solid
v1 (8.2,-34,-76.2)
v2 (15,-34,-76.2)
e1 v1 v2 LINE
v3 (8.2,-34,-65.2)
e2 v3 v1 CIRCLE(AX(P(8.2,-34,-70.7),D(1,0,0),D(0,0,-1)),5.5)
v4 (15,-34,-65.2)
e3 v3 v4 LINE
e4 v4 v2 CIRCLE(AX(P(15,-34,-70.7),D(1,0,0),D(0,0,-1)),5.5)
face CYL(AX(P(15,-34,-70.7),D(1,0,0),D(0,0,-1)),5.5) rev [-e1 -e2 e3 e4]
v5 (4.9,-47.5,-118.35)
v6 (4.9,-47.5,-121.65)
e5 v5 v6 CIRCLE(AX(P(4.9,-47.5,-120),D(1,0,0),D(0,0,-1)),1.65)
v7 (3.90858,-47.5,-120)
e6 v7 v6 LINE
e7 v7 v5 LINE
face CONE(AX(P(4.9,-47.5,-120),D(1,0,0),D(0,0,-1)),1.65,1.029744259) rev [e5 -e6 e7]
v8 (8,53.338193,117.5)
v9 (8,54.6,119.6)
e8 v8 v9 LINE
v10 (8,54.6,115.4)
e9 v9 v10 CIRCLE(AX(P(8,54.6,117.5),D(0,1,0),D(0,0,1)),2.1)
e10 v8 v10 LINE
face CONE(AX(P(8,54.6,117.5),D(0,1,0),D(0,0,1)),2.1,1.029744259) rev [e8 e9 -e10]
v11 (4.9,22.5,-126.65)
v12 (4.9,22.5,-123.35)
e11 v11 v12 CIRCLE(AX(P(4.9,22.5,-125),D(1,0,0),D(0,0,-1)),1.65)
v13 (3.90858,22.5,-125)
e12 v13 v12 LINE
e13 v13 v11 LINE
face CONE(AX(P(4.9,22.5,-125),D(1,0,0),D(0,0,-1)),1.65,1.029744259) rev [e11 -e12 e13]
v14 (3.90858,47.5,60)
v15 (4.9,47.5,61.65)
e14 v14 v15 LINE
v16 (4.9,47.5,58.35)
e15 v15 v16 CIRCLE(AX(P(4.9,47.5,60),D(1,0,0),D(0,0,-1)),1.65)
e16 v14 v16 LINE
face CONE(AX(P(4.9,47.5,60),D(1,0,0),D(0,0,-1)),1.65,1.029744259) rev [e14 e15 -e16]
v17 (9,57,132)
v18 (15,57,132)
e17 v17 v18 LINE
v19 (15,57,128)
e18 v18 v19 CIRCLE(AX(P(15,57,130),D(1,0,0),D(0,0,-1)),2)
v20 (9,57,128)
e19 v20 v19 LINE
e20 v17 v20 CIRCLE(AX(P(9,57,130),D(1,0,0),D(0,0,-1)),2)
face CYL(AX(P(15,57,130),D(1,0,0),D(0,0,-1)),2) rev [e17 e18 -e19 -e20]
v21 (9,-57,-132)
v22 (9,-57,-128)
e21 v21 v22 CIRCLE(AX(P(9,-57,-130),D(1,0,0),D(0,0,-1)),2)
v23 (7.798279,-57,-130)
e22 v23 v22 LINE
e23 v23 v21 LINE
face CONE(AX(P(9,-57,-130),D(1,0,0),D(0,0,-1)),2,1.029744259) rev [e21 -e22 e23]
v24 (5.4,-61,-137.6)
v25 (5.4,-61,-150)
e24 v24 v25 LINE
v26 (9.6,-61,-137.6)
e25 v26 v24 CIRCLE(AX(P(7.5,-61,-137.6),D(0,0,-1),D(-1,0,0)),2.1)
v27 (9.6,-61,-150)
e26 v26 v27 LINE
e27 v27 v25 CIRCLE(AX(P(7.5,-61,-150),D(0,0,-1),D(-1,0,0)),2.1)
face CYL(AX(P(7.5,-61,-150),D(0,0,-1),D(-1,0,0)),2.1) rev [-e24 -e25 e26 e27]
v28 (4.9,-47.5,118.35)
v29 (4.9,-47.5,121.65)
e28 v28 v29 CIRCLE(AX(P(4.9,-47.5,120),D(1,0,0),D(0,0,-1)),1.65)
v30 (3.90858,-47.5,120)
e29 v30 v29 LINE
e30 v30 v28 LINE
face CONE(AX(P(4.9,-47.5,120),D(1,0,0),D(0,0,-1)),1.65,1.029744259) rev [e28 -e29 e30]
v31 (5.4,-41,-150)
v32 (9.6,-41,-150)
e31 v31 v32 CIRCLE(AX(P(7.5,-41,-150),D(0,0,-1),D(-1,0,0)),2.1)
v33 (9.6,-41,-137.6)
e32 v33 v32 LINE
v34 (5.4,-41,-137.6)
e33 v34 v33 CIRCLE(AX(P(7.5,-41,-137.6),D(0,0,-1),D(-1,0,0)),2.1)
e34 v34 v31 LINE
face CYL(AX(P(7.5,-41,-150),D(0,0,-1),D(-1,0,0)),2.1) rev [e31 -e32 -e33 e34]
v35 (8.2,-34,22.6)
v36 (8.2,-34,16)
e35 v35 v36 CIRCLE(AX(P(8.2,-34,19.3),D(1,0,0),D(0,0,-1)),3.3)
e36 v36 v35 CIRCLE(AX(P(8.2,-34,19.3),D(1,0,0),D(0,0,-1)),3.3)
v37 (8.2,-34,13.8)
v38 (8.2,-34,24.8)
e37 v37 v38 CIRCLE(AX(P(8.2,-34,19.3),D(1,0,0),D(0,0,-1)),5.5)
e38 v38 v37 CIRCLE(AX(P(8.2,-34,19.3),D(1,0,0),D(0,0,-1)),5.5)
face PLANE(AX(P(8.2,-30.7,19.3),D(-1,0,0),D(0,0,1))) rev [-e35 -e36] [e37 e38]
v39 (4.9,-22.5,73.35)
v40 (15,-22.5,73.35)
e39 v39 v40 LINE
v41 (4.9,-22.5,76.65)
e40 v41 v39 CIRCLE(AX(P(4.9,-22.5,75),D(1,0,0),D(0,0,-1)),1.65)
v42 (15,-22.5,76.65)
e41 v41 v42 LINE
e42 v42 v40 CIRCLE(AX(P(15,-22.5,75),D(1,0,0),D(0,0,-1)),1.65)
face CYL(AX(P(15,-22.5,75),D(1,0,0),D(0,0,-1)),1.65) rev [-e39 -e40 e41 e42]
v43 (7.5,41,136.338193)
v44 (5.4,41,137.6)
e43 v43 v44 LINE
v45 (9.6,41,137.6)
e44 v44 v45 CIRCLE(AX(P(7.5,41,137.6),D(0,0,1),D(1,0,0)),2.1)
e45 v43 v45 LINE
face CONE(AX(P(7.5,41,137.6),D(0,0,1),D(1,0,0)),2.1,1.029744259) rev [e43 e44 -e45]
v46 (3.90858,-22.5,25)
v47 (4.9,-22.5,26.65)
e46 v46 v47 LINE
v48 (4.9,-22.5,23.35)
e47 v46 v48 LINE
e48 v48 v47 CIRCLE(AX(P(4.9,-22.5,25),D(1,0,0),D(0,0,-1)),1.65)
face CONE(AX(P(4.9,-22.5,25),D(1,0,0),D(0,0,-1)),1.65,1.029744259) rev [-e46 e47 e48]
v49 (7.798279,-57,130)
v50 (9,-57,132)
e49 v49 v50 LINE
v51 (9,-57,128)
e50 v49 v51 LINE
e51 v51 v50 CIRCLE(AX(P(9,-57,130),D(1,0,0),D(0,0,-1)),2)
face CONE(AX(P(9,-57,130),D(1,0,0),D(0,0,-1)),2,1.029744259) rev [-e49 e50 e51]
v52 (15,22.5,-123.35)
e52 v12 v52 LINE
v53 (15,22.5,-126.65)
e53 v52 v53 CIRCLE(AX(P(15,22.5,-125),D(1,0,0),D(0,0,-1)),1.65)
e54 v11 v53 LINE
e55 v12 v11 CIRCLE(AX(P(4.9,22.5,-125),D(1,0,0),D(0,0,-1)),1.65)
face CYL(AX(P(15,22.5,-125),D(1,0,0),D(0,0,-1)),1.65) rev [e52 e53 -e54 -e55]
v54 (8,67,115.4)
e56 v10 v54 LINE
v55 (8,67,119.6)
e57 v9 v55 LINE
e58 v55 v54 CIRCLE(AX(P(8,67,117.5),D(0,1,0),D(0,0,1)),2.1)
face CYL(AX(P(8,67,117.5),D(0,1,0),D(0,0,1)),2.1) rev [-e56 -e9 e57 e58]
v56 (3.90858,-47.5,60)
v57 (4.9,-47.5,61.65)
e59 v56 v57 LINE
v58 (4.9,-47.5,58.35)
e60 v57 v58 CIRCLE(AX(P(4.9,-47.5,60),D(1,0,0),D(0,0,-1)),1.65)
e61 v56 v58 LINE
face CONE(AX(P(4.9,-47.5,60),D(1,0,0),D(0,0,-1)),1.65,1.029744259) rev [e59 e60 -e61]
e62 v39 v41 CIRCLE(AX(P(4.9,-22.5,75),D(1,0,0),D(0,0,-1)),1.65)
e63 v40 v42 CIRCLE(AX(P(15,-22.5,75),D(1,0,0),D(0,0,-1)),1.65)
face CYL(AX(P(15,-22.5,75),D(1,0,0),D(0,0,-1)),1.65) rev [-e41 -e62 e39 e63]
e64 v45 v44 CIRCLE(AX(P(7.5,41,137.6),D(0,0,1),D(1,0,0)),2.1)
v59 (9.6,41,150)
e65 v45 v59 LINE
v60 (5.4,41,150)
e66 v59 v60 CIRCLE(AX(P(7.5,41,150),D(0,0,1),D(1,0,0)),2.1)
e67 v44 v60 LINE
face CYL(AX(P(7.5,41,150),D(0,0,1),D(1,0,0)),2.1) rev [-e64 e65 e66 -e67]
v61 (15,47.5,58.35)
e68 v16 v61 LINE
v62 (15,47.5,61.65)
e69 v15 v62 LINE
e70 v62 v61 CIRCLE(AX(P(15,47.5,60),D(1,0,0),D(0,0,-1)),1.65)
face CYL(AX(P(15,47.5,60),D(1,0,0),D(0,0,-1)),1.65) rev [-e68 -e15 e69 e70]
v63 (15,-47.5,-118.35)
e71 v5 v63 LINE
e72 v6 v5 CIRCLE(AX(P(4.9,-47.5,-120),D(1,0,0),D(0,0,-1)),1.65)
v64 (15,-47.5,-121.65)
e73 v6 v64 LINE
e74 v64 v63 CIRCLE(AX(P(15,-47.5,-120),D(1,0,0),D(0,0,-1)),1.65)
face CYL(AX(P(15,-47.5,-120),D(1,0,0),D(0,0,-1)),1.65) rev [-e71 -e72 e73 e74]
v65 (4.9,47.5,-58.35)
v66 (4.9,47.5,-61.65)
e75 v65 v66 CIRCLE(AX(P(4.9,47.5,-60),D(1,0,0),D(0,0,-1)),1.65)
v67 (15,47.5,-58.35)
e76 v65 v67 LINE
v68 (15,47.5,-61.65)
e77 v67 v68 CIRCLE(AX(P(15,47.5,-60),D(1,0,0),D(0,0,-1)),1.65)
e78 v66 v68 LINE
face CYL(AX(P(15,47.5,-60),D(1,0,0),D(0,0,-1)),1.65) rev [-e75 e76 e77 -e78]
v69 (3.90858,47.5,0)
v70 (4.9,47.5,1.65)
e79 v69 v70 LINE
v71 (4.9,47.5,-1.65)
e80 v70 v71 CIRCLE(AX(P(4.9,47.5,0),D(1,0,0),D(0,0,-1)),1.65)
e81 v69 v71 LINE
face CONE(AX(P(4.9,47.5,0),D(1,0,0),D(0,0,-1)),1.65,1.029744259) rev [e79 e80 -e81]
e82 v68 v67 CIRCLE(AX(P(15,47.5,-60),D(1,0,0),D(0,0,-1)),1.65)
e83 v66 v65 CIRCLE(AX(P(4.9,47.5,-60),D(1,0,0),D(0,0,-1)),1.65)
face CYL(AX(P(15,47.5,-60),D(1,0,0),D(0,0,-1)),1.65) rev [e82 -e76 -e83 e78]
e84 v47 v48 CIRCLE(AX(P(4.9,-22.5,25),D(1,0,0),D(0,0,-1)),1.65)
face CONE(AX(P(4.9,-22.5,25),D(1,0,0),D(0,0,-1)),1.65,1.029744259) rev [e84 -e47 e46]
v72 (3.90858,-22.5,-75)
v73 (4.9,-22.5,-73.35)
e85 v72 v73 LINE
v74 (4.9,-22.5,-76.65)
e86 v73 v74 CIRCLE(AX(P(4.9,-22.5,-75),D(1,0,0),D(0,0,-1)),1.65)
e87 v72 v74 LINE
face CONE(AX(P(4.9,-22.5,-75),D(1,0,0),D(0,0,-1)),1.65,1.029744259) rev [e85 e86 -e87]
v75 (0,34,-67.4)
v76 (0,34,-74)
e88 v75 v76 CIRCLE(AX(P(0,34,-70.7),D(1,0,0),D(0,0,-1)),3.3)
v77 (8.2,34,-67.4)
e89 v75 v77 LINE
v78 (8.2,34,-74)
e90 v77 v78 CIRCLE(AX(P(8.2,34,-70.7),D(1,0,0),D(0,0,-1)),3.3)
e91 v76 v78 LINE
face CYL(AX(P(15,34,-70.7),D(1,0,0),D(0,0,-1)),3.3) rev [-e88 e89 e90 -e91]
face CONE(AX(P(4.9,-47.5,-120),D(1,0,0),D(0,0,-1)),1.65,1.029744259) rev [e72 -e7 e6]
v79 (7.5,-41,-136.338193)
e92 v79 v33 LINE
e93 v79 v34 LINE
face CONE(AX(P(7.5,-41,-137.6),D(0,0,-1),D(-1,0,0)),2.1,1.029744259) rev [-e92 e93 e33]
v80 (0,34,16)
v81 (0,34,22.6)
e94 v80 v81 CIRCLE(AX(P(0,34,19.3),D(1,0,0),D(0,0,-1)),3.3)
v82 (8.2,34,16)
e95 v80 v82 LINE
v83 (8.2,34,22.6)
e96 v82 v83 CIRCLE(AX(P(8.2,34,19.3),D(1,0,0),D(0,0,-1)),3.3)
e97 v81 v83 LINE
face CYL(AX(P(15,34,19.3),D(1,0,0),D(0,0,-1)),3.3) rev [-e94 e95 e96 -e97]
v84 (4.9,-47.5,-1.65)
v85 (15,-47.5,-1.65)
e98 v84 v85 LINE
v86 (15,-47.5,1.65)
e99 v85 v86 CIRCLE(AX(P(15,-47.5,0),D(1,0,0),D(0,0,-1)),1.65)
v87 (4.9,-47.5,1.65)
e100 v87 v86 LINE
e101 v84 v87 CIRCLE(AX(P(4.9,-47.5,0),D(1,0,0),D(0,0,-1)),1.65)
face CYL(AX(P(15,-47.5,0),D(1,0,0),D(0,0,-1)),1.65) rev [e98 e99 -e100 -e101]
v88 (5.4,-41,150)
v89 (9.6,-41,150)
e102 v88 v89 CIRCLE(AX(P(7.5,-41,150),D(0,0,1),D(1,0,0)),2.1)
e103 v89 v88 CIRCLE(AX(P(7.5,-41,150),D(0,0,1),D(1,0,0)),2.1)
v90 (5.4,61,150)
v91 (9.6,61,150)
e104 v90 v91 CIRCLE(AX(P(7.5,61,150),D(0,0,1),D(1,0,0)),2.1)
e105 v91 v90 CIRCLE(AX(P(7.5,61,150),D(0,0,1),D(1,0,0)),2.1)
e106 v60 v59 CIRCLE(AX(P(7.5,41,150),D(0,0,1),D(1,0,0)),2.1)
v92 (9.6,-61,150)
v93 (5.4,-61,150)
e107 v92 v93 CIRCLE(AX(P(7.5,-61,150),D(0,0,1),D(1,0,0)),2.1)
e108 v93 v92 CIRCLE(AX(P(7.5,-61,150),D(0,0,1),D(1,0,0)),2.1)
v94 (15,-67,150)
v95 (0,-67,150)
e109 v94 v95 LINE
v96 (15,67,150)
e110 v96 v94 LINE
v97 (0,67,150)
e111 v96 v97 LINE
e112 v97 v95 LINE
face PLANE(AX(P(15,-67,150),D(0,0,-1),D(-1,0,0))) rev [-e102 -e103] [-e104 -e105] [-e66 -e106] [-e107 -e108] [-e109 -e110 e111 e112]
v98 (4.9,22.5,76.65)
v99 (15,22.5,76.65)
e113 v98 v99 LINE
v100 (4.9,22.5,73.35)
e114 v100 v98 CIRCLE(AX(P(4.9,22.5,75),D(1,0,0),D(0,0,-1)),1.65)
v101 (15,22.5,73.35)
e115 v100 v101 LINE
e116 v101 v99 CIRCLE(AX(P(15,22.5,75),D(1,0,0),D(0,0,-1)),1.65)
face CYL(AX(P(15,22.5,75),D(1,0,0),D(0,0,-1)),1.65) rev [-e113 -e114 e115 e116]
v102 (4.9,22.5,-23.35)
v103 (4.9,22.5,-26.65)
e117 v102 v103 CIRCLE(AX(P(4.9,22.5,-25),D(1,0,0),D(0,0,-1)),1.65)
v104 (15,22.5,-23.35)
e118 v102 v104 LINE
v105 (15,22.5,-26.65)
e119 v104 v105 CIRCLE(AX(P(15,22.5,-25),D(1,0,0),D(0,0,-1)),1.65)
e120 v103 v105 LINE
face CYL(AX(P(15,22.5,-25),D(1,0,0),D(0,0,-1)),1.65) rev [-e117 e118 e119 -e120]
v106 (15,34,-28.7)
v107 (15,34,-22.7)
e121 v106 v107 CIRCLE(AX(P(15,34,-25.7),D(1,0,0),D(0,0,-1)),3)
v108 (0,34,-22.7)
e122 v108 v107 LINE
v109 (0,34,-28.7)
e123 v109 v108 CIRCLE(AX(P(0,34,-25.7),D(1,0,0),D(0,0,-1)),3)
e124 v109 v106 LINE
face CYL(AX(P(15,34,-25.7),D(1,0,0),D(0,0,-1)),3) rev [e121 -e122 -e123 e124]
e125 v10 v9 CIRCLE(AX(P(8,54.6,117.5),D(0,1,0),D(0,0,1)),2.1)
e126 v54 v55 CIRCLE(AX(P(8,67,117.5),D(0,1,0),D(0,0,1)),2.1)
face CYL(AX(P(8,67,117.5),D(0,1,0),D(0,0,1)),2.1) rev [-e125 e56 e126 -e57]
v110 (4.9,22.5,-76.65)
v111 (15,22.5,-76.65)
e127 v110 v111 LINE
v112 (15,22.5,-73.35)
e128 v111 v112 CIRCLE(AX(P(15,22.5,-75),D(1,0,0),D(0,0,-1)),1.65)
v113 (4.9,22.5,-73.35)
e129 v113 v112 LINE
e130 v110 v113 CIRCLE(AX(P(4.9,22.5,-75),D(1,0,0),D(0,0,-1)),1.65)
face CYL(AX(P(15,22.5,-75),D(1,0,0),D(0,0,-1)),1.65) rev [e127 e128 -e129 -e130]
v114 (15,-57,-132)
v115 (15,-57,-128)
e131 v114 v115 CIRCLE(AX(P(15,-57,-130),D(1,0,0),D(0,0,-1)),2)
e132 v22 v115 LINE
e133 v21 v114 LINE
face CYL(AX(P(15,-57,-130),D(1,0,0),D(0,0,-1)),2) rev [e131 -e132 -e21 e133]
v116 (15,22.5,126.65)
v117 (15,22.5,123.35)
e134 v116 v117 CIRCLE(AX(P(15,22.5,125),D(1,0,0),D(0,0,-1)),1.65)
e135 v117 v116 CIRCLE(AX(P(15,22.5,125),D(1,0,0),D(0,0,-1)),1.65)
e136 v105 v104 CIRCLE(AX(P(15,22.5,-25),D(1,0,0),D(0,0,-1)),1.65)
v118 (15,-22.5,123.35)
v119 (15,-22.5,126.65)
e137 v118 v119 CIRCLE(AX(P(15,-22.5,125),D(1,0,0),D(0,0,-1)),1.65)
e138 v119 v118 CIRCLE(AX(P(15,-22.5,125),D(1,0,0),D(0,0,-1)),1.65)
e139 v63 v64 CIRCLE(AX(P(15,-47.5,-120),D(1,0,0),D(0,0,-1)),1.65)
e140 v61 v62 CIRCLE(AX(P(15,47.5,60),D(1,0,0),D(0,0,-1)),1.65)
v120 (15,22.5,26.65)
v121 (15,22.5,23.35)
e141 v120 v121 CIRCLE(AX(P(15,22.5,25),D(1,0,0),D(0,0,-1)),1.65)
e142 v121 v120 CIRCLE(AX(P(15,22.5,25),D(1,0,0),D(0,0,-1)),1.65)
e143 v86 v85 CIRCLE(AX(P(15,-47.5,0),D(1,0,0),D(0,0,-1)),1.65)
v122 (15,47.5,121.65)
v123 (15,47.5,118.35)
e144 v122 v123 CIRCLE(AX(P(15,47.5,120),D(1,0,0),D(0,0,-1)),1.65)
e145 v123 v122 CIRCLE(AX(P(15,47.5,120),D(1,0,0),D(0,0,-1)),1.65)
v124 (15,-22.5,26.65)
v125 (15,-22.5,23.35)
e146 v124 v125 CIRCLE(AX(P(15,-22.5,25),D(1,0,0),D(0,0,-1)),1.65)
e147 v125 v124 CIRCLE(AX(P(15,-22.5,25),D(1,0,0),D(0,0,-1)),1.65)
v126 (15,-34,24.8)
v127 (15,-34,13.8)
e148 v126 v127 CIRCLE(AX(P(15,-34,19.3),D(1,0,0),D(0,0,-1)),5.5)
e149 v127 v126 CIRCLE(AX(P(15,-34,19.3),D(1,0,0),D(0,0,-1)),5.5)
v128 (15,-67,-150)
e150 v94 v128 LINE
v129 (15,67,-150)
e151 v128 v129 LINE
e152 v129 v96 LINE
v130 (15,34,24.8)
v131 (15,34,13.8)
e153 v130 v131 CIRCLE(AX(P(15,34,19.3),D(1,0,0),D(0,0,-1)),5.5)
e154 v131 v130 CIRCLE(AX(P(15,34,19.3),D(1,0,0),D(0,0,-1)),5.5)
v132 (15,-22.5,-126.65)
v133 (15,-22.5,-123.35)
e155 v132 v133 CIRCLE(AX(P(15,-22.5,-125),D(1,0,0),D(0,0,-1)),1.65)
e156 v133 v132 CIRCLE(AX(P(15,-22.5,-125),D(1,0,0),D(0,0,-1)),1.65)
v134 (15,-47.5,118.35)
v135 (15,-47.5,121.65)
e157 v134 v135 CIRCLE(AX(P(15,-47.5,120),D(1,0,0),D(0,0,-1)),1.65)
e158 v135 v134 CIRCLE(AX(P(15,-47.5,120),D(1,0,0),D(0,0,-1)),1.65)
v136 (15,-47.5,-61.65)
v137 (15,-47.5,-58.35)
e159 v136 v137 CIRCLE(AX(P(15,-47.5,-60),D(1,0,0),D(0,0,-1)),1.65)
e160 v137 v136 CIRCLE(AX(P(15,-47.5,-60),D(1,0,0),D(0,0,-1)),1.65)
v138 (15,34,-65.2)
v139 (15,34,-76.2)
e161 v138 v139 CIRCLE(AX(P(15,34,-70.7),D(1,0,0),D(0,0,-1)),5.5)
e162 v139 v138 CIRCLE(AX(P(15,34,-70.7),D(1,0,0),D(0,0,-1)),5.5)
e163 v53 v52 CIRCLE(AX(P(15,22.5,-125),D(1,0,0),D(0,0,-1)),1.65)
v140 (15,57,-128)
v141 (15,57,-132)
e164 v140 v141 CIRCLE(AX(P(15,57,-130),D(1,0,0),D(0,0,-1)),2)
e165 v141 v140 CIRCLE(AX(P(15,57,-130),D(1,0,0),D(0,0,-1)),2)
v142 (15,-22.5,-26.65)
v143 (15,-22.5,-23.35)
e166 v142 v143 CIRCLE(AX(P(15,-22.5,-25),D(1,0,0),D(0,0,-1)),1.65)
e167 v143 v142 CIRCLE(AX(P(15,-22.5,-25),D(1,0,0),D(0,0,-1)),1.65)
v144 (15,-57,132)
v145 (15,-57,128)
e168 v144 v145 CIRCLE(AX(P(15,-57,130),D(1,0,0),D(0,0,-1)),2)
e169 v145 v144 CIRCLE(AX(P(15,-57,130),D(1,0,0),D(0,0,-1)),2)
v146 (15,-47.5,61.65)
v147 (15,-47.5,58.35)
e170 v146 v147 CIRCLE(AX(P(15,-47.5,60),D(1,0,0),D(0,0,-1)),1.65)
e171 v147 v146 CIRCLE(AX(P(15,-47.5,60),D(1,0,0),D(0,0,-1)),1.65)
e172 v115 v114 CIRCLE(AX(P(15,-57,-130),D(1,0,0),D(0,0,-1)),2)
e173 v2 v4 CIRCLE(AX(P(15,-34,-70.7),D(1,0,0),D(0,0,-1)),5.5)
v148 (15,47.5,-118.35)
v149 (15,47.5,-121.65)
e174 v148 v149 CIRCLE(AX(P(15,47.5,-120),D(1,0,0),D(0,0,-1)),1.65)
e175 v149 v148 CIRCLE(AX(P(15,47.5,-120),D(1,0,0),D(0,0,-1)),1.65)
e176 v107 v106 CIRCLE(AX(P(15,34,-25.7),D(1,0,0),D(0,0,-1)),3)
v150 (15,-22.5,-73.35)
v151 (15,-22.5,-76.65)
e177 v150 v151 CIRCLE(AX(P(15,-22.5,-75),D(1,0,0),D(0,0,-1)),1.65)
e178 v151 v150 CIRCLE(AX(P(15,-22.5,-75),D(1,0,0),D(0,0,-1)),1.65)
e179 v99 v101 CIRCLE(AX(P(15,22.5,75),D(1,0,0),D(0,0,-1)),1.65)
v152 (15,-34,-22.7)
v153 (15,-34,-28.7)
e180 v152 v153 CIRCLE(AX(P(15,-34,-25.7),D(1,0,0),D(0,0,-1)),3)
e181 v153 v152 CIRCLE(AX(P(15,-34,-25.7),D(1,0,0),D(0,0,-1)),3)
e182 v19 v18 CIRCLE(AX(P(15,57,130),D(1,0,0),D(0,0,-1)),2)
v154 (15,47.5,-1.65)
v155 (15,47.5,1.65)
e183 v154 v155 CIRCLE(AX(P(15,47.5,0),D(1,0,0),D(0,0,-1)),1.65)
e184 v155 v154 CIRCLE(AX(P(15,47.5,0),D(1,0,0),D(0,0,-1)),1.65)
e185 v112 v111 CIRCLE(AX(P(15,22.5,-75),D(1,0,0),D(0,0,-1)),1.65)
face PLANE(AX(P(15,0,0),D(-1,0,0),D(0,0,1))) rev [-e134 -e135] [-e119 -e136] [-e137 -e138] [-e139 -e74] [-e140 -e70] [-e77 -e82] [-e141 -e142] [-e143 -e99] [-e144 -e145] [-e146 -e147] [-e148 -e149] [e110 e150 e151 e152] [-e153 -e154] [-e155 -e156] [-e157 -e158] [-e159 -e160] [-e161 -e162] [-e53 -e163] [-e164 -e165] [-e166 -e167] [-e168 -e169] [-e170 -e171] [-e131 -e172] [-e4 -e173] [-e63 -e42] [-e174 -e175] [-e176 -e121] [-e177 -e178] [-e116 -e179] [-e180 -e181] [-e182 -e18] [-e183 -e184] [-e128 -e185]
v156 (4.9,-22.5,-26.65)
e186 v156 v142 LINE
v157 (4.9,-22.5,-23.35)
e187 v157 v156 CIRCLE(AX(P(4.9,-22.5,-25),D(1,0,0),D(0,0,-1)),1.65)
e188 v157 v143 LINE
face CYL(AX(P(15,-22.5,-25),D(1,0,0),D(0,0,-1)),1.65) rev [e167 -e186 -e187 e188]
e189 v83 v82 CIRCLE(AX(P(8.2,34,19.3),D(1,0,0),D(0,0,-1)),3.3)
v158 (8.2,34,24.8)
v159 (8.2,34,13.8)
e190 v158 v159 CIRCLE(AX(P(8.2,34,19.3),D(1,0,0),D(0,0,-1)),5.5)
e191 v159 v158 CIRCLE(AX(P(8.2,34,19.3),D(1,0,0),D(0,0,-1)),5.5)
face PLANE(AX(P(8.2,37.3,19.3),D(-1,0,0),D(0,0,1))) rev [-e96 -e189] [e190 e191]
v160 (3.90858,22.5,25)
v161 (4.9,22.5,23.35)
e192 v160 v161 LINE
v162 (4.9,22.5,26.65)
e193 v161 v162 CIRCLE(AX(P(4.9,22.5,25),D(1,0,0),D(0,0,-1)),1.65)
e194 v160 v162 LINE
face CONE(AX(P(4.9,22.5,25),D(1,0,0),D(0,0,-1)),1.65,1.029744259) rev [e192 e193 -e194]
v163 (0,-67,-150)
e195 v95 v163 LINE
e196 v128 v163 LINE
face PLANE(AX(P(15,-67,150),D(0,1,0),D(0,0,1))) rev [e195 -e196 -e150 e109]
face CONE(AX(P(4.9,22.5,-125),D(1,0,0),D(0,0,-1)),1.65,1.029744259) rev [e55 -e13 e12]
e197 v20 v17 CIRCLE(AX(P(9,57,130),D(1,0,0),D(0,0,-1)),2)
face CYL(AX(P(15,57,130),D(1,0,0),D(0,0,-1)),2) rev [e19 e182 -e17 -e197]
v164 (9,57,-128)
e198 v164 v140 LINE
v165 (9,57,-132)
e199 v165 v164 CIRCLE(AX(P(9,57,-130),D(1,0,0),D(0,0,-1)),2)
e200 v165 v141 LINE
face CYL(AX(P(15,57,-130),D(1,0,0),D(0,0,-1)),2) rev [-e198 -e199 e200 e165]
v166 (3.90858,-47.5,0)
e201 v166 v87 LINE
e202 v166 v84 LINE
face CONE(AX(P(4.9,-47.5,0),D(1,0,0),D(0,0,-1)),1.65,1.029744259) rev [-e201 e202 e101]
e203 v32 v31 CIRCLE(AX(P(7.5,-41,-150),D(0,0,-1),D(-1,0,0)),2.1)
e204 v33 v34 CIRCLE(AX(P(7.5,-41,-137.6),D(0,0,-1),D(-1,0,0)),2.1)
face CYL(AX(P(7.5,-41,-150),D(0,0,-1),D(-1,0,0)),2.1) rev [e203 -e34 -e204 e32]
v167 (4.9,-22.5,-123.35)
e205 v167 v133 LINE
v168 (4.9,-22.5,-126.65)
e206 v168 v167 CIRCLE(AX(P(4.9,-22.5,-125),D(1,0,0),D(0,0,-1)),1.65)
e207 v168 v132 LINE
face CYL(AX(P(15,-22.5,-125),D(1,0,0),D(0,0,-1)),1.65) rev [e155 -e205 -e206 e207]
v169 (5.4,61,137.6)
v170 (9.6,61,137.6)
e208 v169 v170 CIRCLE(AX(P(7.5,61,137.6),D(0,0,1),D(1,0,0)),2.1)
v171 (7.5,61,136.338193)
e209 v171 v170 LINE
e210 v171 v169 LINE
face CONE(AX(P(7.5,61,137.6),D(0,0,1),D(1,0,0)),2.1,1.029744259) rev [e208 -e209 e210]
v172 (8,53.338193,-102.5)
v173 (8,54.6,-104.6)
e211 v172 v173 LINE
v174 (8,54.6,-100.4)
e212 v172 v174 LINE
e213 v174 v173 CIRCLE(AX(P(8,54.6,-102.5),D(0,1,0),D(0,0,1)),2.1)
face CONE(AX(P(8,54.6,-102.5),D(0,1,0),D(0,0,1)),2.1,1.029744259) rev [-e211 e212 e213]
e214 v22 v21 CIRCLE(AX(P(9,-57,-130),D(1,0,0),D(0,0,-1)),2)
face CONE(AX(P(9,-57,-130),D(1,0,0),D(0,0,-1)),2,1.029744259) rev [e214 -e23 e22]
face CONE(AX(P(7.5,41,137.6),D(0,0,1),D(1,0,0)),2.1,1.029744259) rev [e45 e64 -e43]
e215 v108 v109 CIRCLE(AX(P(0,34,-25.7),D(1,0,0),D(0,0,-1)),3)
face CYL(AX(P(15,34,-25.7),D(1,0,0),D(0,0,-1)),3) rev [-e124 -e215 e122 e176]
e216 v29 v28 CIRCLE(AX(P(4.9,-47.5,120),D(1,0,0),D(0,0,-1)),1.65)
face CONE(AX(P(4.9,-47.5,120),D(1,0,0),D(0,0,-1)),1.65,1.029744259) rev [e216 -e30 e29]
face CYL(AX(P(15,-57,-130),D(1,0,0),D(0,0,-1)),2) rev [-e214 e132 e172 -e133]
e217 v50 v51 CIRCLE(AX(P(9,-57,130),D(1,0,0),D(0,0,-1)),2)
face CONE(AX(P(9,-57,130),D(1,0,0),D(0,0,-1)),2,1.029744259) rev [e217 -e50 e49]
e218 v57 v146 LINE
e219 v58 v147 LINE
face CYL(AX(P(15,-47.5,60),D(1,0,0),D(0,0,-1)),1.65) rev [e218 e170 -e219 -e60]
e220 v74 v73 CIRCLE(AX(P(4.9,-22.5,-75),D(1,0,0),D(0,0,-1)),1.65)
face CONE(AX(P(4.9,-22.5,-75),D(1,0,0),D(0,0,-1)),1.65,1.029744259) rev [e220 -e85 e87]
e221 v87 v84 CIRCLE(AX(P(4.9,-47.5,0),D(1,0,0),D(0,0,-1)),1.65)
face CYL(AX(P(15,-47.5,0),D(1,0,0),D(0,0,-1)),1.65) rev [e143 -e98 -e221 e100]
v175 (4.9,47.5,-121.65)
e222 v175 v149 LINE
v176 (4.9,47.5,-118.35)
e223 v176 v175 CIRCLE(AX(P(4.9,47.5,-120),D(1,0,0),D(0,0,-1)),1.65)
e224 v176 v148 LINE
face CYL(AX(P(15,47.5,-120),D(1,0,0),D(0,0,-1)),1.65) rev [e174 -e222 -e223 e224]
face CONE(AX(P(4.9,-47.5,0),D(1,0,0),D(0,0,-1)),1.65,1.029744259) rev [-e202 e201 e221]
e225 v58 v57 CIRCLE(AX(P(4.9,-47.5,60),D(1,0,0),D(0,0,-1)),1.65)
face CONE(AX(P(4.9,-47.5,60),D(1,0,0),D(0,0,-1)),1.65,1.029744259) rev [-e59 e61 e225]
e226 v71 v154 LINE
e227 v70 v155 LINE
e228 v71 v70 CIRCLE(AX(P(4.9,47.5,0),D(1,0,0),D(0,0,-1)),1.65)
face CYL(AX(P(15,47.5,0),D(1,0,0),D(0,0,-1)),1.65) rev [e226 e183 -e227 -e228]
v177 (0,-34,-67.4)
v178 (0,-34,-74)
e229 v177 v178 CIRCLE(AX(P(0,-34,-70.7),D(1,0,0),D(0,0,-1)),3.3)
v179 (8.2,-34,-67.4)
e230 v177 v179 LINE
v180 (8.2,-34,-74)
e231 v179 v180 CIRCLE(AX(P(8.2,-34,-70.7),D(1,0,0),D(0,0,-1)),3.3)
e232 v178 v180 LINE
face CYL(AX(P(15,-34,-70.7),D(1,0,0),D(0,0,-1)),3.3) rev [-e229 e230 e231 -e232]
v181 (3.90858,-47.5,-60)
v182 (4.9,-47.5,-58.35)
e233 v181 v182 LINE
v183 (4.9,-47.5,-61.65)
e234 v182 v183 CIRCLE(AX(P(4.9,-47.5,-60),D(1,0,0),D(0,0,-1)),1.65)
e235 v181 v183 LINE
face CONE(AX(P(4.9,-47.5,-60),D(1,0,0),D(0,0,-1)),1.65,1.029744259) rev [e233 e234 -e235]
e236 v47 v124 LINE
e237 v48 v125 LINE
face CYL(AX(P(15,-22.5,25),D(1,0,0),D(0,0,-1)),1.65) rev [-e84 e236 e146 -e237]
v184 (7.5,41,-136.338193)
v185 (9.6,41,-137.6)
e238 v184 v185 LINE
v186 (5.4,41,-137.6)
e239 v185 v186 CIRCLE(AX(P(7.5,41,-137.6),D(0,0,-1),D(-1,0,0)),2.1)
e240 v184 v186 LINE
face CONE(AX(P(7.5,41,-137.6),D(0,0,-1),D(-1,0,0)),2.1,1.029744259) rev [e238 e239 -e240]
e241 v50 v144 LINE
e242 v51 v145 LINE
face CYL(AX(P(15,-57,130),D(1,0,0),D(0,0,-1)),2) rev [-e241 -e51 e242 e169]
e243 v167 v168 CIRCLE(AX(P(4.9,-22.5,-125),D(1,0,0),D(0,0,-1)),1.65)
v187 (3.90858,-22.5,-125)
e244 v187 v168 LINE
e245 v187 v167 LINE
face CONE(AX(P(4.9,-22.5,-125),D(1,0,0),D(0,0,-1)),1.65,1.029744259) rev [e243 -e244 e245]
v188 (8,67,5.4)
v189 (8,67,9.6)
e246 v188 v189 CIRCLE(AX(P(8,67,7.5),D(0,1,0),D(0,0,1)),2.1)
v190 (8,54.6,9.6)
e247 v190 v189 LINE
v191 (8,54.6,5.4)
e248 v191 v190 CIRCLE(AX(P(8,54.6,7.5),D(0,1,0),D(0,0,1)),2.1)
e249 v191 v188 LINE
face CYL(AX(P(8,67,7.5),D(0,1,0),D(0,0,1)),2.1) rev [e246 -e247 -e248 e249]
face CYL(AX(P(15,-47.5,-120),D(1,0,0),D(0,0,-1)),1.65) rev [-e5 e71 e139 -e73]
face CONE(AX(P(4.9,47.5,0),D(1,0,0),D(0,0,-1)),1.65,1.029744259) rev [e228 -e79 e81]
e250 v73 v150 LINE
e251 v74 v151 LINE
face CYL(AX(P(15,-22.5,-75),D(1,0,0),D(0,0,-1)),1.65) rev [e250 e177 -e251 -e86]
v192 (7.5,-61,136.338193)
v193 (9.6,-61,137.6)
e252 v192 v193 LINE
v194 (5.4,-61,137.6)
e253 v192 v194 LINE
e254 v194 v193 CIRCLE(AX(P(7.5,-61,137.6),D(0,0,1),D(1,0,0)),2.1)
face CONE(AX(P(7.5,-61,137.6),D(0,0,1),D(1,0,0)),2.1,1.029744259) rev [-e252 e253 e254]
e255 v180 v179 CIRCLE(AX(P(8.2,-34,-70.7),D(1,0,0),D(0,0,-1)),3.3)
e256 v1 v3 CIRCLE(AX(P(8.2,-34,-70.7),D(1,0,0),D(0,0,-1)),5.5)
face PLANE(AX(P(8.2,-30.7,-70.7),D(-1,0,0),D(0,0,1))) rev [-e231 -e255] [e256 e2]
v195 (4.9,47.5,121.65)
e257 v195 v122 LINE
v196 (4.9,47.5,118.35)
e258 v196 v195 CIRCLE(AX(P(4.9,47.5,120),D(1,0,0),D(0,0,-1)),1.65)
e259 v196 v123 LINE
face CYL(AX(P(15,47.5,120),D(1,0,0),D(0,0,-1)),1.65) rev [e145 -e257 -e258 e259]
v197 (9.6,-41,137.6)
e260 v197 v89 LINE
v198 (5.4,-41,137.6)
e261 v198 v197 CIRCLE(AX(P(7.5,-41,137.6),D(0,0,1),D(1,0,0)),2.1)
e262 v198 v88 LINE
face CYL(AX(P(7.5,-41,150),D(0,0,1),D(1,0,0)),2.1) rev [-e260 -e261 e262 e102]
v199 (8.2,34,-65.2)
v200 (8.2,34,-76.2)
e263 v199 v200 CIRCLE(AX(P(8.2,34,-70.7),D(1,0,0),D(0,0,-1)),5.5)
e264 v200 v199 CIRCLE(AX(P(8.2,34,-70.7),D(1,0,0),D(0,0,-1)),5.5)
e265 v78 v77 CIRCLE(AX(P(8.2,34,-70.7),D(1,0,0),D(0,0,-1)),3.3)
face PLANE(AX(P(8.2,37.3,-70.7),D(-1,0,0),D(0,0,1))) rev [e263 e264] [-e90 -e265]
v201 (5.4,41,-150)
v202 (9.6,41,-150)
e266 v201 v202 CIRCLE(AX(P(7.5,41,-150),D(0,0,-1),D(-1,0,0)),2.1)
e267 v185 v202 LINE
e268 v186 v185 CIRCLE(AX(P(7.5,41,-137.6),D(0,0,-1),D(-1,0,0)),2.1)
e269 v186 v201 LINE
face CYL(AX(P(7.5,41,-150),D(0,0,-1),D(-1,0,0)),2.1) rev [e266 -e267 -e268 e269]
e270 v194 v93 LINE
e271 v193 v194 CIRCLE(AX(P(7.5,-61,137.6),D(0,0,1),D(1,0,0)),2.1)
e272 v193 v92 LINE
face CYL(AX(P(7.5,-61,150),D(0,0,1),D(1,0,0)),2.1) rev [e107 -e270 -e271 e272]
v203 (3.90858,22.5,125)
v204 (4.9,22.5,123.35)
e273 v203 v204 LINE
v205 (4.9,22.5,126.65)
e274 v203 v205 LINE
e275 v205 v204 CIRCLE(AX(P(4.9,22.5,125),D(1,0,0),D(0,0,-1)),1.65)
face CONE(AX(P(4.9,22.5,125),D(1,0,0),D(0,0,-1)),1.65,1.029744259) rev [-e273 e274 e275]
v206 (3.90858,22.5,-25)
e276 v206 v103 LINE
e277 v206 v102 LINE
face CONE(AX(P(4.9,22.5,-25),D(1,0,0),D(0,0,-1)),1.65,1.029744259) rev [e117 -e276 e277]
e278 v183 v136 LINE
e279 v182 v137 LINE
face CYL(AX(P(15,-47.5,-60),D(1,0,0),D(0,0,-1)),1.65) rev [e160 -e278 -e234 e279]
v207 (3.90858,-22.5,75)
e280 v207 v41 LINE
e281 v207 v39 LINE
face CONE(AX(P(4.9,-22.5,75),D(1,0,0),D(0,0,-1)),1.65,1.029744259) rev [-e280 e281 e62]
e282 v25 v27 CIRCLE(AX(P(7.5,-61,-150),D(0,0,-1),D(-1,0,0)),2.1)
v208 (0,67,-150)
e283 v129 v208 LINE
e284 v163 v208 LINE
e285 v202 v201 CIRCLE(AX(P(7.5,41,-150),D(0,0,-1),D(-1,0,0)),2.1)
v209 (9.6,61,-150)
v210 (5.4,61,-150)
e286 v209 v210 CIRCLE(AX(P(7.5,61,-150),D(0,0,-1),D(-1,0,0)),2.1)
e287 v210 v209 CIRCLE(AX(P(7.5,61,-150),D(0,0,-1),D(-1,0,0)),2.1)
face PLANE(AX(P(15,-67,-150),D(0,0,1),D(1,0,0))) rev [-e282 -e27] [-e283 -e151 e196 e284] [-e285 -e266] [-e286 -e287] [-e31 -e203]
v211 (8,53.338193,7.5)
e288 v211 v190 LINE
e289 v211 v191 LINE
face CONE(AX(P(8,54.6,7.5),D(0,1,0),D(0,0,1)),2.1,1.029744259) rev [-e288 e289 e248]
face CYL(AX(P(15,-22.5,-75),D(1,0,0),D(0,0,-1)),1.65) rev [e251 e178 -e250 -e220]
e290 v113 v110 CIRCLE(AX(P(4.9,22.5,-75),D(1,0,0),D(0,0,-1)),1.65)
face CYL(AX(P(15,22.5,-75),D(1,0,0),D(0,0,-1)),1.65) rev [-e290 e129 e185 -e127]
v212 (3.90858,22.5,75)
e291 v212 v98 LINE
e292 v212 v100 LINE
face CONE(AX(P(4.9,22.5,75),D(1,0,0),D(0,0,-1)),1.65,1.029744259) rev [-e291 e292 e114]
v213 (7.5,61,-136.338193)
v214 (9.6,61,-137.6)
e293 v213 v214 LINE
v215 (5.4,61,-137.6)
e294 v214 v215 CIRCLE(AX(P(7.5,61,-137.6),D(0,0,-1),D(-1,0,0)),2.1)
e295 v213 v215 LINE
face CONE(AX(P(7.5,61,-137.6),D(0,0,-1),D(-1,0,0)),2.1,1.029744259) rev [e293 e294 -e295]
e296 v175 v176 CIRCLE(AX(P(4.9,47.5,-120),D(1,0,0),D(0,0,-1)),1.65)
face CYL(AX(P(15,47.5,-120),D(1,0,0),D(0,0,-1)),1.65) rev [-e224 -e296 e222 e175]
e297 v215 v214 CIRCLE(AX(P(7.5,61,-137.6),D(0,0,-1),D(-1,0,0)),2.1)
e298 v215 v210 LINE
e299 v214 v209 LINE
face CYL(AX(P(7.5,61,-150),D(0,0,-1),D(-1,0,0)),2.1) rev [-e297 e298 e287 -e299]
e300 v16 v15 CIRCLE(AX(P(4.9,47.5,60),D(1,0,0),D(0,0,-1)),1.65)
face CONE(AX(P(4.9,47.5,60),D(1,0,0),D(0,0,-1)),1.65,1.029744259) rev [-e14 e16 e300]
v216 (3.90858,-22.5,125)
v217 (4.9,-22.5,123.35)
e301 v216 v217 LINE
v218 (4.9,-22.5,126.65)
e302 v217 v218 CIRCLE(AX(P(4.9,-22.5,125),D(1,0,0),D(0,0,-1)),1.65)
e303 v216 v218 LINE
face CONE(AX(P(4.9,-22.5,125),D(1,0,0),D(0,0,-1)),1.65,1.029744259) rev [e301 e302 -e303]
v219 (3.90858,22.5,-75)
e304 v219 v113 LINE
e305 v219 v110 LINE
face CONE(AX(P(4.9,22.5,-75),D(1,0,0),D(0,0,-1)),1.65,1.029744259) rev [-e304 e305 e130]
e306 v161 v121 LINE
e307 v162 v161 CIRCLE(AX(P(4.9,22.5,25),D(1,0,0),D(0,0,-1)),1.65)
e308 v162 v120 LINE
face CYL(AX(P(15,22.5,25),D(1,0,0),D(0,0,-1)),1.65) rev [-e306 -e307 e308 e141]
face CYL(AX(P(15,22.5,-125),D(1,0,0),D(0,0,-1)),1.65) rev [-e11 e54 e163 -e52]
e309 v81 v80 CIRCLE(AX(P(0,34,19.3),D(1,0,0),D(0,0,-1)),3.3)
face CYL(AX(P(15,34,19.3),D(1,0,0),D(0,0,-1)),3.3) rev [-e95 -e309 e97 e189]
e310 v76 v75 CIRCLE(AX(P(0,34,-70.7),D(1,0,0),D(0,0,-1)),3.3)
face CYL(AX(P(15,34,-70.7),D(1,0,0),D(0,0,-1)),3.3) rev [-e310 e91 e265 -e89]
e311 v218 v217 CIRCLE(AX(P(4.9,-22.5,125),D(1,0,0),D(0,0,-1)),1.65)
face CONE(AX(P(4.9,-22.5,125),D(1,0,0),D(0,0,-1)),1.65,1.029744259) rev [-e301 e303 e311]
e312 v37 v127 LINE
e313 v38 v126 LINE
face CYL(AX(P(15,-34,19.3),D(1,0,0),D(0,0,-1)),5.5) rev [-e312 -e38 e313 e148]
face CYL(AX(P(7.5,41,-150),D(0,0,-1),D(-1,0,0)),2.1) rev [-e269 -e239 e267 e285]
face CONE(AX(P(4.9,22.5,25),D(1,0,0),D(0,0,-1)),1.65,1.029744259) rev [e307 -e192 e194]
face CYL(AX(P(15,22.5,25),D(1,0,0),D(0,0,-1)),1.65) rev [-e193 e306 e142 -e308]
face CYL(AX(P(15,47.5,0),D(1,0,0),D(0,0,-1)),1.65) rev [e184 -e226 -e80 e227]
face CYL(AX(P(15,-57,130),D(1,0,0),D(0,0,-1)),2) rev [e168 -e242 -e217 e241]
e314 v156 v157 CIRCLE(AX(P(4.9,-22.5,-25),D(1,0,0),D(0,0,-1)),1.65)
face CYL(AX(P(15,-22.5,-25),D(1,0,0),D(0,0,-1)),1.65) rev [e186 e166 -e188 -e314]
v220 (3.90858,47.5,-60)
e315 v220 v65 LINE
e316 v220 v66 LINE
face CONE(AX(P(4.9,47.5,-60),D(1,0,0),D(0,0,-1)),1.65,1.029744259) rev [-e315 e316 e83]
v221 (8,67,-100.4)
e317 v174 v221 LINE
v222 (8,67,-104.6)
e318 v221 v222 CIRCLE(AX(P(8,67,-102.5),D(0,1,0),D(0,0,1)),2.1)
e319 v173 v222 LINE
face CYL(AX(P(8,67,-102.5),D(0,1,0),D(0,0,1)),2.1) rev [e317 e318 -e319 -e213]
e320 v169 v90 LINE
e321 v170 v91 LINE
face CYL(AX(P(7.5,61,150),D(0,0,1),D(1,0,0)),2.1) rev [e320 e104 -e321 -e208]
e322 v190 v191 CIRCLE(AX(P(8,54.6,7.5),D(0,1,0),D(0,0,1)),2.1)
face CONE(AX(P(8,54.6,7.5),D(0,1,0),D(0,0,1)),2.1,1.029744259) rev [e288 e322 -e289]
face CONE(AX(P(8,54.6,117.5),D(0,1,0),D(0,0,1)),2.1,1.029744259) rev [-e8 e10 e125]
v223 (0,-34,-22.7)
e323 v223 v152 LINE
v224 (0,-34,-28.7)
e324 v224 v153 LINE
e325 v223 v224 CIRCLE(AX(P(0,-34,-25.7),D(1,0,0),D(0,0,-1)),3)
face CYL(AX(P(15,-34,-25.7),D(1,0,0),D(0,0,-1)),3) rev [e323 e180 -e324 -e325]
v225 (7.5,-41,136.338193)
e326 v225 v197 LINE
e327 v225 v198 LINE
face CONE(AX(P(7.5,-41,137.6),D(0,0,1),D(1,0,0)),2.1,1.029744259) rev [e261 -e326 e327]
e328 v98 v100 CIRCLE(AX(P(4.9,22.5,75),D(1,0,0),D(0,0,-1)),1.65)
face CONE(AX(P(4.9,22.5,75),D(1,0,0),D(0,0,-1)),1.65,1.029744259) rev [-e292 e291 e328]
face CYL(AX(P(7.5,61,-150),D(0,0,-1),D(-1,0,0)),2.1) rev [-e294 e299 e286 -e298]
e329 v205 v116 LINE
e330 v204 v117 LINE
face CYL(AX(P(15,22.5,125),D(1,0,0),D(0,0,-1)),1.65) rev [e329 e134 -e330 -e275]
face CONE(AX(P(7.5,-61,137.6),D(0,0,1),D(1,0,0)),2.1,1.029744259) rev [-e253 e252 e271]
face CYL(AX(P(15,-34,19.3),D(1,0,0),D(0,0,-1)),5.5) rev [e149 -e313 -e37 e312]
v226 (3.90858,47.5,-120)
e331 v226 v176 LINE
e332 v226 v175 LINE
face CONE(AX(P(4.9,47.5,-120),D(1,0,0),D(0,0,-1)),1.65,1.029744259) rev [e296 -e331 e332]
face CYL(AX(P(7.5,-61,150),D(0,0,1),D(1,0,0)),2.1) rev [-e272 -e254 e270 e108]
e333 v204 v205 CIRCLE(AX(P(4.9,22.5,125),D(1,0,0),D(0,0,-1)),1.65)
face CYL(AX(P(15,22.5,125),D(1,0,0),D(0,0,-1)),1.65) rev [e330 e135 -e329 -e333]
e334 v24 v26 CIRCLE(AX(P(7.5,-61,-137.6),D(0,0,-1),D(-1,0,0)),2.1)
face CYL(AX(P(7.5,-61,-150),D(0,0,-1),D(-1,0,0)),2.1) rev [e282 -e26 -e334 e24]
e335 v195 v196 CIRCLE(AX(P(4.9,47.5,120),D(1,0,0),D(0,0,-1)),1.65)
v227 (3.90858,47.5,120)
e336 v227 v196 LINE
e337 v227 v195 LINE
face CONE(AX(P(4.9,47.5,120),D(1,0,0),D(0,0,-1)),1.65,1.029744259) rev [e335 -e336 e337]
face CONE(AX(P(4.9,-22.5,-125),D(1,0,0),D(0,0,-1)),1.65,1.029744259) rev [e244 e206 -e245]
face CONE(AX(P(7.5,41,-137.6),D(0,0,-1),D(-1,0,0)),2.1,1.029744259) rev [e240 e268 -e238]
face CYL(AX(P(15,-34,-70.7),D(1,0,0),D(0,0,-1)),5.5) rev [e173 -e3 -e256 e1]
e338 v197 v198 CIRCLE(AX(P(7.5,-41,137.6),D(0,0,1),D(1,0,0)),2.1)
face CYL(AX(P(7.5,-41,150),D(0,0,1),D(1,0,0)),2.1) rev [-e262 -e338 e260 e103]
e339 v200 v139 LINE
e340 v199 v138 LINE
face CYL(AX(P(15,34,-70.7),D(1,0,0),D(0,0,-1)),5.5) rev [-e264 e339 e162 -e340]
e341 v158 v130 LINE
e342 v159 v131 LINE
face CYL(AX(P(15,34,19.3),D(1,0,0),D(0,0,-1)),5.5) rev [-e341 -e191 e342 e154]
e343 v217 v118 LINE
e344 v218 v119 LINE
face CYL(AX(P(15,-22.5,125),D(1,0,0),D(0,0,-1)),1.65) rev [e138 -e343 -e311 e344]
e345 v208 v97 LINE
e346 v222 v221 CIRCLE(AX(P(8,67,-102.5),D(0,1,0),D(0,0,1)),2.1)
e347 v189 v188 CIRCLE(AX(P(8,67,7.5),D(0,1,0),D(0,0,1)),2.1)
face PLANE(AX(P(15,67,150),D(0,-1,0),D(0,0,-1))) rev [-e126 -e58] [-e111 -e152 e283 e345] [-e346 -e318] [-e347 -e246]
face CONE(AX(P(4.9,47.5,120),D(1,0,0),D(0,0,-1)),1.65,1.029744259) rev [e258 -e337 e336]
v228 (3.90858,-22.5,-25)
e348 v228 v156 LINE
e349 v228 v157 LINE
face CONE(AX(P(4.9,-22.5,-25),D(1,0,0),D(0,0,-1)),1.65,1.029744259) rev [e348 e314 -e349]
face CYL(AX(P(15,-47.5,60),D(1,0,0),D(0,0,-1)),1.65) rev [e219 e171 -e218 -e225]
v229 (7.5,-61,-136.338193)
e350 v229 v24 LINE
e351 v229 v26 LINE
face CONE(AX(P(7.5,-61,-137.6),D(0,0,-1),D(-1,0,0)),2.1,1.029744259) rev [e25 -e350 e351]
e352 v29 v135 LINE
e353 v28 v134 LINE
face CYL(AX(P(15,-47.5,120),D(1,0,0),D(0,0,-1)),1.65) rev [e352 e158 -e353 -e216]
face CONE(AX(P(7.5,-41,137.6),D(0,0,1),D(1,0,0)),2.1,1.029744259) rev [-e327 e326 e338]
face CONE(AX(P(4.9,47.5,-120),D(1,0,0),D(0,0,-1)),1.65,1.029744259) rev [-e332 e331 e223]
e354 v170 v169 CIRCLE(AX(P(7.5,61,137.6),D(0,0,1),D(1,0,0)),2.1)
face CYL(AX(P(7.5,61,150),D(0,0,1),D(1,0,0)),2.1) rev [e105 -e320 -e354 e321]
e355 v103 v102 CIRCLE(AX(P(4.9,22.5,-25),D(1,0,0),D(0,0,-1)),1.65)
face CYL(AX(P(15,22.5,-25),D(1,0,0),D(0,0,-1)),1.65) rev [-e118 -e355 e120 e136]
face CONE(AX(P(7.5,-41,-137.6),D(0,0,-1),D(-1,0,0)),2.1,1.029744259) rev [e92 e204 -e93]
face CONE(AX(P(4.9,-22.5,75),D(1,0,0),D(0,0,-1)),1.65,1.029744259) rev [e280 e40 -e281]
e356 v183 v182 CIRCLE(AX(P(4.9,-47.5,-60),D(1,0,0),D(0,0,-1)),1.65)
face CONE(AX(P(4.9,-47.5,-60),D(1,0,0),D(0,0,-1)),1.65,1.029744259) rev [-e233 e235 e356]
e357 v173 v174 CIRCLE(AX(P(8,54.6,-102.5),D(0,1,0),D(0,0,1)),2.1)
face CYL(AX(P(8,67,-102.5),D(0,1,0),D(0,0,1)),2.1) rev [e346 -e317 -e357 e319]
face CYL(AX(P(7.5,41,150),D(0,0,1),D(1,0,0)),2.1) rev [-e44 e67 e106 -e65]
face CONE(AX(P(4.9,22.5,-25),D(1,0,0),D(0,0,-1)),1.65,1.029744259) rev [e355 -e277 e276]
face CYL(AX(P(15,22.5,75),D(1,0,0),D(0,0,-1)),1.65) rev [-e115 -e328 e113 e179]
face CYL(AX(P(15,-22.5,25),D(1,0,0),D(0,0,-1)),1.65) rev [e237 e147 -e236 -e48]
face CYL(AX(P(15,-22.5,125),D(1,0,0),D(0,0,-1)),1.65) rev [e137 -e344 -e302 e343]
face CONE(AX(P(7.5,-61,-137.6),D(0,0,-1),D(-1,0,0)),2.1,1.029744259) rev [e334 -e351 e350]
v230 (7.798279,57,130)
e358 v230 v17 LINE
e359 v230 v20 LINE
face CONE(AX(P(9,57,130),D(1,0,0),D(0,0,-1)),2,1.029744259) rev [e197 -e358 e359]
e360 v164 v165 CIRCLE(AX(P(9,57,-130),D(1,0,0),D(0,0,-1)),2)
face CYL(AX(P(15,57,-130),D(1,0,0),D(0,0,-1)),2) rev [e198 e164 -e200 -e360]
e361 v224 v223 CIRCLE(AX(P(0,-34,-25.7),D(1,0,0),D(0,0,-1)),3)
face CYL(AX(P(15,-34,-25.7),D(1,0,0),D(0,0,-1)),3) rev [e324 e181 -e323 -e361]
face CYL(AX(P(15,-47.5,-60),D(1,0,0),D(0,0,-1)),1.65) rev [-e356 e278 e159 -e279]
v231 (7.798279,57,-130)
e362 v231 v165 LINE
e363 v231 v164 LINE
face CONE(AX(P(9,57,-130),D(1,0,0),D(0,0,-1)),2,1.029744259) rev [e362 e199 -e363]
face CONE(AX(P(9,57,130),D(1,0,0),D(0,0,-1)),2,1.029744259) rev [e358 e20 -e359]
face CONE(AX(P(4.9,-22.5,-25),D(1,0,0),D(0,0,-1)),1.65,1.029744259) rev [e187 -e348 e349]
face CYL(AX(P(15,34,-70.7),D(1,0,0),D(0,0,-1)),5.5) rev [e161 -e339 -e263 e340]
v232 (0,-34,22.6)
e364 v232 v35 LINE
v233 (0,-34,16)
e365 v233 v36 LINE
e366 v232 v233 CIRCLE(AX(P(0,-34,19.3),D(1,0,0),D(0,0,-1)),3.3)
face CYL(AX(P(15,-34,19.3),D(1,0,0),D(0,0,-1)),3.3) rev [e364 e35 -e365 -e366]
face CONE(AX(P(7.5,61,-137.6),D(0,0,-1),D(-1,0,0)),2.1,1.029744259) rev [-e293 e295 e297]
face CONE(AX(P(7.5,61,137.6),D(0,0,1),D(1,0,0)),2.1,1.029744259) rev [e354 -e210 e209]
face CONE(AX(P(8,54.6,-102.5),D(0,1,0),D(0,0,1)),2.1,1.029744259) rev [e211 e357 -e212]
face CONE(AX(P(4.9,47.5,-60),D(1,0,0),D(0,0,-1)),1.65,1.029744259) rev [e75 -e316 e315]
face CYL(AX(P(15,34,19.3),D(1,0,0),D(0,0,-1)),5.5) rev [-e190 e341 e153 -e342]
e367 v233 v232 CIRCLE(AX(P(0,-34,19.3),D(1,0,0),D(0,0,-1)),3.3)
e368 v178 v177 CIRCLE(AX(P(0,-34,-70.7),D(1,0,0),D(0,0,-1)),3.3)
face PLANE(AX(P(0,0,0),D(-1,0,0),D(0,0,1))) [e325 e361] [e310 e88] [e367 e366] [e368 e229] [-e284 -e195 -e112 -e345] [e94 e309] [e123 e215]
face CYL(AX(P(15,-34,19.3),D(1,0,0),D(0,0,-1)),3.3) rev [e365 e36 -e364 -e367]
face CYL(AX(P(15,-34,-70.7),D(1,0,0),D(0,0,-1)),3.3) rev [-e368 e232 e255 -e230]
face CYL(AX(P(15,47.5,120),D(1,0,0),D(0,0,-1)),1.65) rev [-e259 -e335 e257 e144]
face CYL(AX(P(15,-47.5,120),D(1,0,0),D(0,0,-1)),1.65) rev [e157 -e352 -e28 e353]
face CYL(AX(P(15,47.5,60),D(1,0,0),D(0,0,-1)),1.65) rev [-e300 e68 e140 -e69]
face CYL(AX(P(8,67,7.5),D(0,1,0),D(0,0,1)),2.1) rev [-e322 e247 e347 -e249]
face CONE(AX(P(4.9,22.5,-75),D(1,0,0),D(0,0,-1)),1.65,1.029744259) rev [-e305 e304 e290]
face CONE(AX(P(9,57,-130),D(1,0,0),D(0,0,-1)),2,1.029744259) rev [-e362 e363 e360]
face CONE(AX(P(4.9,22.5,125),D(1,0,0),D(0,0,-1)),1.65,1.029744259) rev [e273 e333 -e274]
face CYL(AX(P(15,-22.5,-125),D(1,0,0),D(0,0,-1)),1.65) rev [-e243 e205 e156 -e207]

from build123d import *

# Parameters (mm, degrees)
SKETCH1_W                                            = 300
SKETCH1_H                                            = 134
BOSS_EXTRUDE1_DEPTH                                  = 15
M4_TAPPED_HOLE1_D                                    = 3.3
M4_TAPPED_HOLE1_DEPTH                                = 10.1
M4_TAPPED_HOLE1_TIP                                  = 0.991420021
M4_TAPPED_HOLE2_D                                    = 3.3
M4_TAPPED_HOLE2_DEPTH                                = 10.1
M4_TAPPED_HOLE2_TIP                                  = 0.991420021
M5_TAPPED_HOLE1_AT_2_COUNT                           = 2
M5_TAPPED_HOLE1_AT_2_PITCH                           = 20
M5_TAPPED_HOLE1_AT_3_COUNT                           = 2
M5_TAPPED_HOLE1_AT_3_PITCH                           = 102
M5_TAPPED_HOLE1_AT_4_COUNT                           = 2
M5_TAPPED_HOLE1_AT_4_PITCH                           = 122
F_4_0MM_DOWEL_HOLE1_D                                = 4
F_4_0MM_DOWEL_HOLE1_DEPTH                            = 6
F_4_0MM_DOWEL_HOLE1_TIP                              = 1.201721238
CBORE_FOR_M6_HEXAGON_SOCKET_HEAD_CAP_SCR_D           = 6.6
CBORE_FOR_M6_HEXAGON_SOCKET_HEAD_CAP_SCR_CBORE_D     = 11
CBORE_FOR_M6_HEXAGON_SOCKET_HEAD_CAP_SCR_CBORE_DEPTH = 6.8
F_6_0MM_DOWEL_HOLE1_D                                = 6
M5_TAPPED_HOLE2_D                                    = 4.2
M5_TAPPED_HOLE2_DEPTH                                = 12.4
M5_TAPPED_HOLE2_TIP                                  = 1.2618073


with BuildPart() as part:
    # Sketch1 → Boss-Extrude1 (new body)
    with BuildSketch(Plane(origin=(0, 0, 0), x_dir=(0, 0, -1), z_dir=(1, 0, 0))):
        Rectangle(SKETCH1_W, SKETCH1_H)
    extrude(amount=BOSS_EXTRUDE1_DEPTH)

    # M4 Tapped Hole1
    with Locations(Plane(origin=(15, 0, 0), x_dir=(0, 0, -1), z_dir=(1, 0, 0))):
        with Locations((-120, -47.5), (-60, -47.5), (0, -47.5), (60, -47.5), (120, -47.5), (120, 47.5), (60, 47.5), (0, 47.5), (-60, 47.5), (-120, 47.5)):
            Hole(M4_TAPPED_HOLE1_D / 2, depth=M4_TAPPED_HOLE1_DEPTH)
            with Locations((0, 0, -(M4_TAPPED_HOLE1_DEPTH + M4_TAPPED_HOLE1_TIP / 2))):  # 118° drill point
                Cone(0, M4_TAPPED_HOLE1_D / 2, M4_TAPPED_HOLE1_TIP, mode=Mode.SUBTRACT)

    # M4 Tapped Hole2
    with Locations(Plane(origin=(15, 0, 0), x_dir=(0, 0, -1), z_dir=(1, 0, 0))):
        with Locations((-125, 22.5), (-75, 22.5), (-25, 22.5), (-125, -22.5), (-75, -22.5), (-25, -22.5), (25, 22.5), (75, 22.5), (125, 22.5), (125, -22.5), (75, -22.5), (25, -22.5)):
            Hole(M4_TAPPED_HOLE2_D / 2, depth=M4_TAPPED_HOLE2_DEPTH)
            with Locations((0, 0, -(M4_TAPPED_HOLE2_DEPTH + M4_TAPPED_HOLE2_TIP / 2))):  # 118° drill point
                Cone(0, M4_TAPPED_HOLE2_D / 2, M4_TAPPED_HOLE2_TIP, mode=Mode.SUBTRACT)

    # Sketch7 → M5 Tapped Hole1 (revolve, cut)
    with BuildSketch(Plane(origin=(7.5, -61, -150), x_dir=(0, 1, 0), z_dir=(1, 0, 0))):
        Polygon((0, 0), (0, 13.6618073), (2.1, 12.4), (2.1, 0), align=None)
    m5_tapped_hole1 = revolve(axis=Axis((7.5, -61, -156.35), (0, 0, 1)), mode=Mode.SUBTRACT)

    # M5 Tapped Hole1 at 2: M5 Tapped Hole1 ×2
    with Locations(*[(0, i * M5_TAPPED_HOLE1_AT_2_PITCH, 0) for i in range(1, M5_TAPPED_HOLE1_AT_2_COUNT)]):
        add(m5_tapped_hole1, mode=Mode.SUBTRACT)

    # M5 Tapped Hole1 at 3: M5 Tapped Hole1 ×2
    with Locations(*[(0, i * M5_TAPPED_HOLE1_AT_3_PITCH, 0) for i in range(1, M5_TAPPED_HOLE1_AT_3_COUNT)]):
        add(m5_tapped_hole1, mode=Mode.SUBTRACT)

    # M5 Tapped Hole1 at 4: M5 Tapped Hole1 ×2
    with Locations(*[(0, i * M5_TAPPED_HOLE1_AT_4_PITCH, 0) for i in range(1, M5_TAPPED_HOLE1_AT_4_COUNT)]):
        add(m5_tapped_hole1, mode=Mode.SUBTRACT)

    # Mirror1: M5 Tapped Hole1 across plane
    add(m5_tapped_hole1.mirror(Plane.XY), mode=Mode.SUBTRACT)

    # Mirror1 copy 1 sketch → Mirror1 copy 1 (revolve, cut)
    with BuildSketch(Plane(origin=(7.5, -41, 150), x_dir=(0, 1, 0), z_dir=(1, 0, 0))):
        Polygon((0, 0), (0, -13.6618073), (2.1, -12.4), (2.1, 0), align=None)
    revolve(axis=Axis((7.5, -41, 156.35), (0, 0, 1)), mode=Mode.SUBTRACT)

    # Mirror1 copy 2 sketch → Mirror1 copy 2 (revolve, cut)
    with BuildSketch(Plane(origin=(7.5, 41, 150), x_dir=(0, 1, 0), z_dir=(1, 0, 0))):
        Polygon((0, 0), (0, -13.6618073), (2.1, -12.4), (2.1, 0), align=None)
    revolve(axis=Axis((7.5, 41, 156.35), (0, 0, 1)), mode=Mode.SUBTRACT)

    # Mirror1 copy 3 sketch → Mirror1 copy 3 (revolve, cut)
    with BuildSketch(Plane(origin=(7.5, 61, 150), x_dir=(0, 1, 0), z_dir=(1, 0, 0))):
        Polygon((0, 0), (0, -13.6618073), (2.1, -12.4), (2.1, 0), align=None)
    revolve(axis=Axis((7.5, 61, 156.35), (0, 0, 1)), mode=Mode.SUBTRACT)

    # Ø4.0mm Dowel Hole1
    with Locations(Plane(origin=(15, 0, 0), x_dir=(0, 0, -1), z_dir=(1, 0, 0))):
        with Locations((130, 57), (-130, 57), (-130, -57), (130, -57)):
            Hole(F_4_0MM_DOWEL_HOLE1_D / 2, depth=F_4_0MM_DOWEL_HOLE1_DEPTH)
            with Locations((0, 0, -(F_4_0MM_DOWEL_HOLE1_DEPTH + F_4_0MM_DOWEL_HOLE1_TIP / 2))):  # 118° drill point
                Cone(0, F_4_0MM_DOWEL_HOLE1_D / 2, F_4_0MM_DOWEL_HOLE1_TIP, mode=Mode.SUBTRACT)

    # CBORE for M6 Hexagon socket head cap screws1 (through all)
    with Locations(Plane(origin=(15, 0, 0), x_dir=(0, 0, -1), z_dir=(1, 0, 0))):
        with Locations((70.7, 34), (-19.3, 34), (-19.3, -34), (70.7, -34)):
            CounterBoreHole(CBORE_FOR_M6_HEXAGON_SOCKET_HEAD_CAP_SCR_D / 2, CBORE_FOR_M6_HEXAGON_SOCKET_HEAD_CAP_SCR_CBORE_D / 2, CBORE_FOR_M6_HEXAGON_SOCKET_HEAD_CAP_SCR_CBORE_DEPTH)

    # Ø6.0mm Dowel Hole1 (through all)
    with Locations(Plane(origin=(15, 0, 0), x_dir=(0, 0, -1), z_dir=(1, 0, 0))):
        with Locations((25.7, 34), (25.7, -34)):
            Hole(F_6_0MM_DOWEL_HOLE1_D / 2)

    # M5 Tapped Hole2
    with Locations(Plane(origin=(0, 67, 0), x_dir=(-1, 0, 0), z_dir=(0, 1, 0))):
        with Locations((-8, 117.5), (-8, -102.5), (-8, 7.5)):
            Hole(M5_TAPPED_HOLE2_D / 2, depth=M5_TAPPED_HOLE2_DEPTH)
            with Locations((0, 0, -(M5_TAPPED_HOLE2_DEPTH + M5_TAPPED_HOLE2_TIP / 2))):  # 118° drill point
                Cone(0, M5_TAPPED_HOLE2_D / 2, M5_TAPPED_HOLE2_TIP, mode=Mode.SUBTRACT)


solid = part.part
